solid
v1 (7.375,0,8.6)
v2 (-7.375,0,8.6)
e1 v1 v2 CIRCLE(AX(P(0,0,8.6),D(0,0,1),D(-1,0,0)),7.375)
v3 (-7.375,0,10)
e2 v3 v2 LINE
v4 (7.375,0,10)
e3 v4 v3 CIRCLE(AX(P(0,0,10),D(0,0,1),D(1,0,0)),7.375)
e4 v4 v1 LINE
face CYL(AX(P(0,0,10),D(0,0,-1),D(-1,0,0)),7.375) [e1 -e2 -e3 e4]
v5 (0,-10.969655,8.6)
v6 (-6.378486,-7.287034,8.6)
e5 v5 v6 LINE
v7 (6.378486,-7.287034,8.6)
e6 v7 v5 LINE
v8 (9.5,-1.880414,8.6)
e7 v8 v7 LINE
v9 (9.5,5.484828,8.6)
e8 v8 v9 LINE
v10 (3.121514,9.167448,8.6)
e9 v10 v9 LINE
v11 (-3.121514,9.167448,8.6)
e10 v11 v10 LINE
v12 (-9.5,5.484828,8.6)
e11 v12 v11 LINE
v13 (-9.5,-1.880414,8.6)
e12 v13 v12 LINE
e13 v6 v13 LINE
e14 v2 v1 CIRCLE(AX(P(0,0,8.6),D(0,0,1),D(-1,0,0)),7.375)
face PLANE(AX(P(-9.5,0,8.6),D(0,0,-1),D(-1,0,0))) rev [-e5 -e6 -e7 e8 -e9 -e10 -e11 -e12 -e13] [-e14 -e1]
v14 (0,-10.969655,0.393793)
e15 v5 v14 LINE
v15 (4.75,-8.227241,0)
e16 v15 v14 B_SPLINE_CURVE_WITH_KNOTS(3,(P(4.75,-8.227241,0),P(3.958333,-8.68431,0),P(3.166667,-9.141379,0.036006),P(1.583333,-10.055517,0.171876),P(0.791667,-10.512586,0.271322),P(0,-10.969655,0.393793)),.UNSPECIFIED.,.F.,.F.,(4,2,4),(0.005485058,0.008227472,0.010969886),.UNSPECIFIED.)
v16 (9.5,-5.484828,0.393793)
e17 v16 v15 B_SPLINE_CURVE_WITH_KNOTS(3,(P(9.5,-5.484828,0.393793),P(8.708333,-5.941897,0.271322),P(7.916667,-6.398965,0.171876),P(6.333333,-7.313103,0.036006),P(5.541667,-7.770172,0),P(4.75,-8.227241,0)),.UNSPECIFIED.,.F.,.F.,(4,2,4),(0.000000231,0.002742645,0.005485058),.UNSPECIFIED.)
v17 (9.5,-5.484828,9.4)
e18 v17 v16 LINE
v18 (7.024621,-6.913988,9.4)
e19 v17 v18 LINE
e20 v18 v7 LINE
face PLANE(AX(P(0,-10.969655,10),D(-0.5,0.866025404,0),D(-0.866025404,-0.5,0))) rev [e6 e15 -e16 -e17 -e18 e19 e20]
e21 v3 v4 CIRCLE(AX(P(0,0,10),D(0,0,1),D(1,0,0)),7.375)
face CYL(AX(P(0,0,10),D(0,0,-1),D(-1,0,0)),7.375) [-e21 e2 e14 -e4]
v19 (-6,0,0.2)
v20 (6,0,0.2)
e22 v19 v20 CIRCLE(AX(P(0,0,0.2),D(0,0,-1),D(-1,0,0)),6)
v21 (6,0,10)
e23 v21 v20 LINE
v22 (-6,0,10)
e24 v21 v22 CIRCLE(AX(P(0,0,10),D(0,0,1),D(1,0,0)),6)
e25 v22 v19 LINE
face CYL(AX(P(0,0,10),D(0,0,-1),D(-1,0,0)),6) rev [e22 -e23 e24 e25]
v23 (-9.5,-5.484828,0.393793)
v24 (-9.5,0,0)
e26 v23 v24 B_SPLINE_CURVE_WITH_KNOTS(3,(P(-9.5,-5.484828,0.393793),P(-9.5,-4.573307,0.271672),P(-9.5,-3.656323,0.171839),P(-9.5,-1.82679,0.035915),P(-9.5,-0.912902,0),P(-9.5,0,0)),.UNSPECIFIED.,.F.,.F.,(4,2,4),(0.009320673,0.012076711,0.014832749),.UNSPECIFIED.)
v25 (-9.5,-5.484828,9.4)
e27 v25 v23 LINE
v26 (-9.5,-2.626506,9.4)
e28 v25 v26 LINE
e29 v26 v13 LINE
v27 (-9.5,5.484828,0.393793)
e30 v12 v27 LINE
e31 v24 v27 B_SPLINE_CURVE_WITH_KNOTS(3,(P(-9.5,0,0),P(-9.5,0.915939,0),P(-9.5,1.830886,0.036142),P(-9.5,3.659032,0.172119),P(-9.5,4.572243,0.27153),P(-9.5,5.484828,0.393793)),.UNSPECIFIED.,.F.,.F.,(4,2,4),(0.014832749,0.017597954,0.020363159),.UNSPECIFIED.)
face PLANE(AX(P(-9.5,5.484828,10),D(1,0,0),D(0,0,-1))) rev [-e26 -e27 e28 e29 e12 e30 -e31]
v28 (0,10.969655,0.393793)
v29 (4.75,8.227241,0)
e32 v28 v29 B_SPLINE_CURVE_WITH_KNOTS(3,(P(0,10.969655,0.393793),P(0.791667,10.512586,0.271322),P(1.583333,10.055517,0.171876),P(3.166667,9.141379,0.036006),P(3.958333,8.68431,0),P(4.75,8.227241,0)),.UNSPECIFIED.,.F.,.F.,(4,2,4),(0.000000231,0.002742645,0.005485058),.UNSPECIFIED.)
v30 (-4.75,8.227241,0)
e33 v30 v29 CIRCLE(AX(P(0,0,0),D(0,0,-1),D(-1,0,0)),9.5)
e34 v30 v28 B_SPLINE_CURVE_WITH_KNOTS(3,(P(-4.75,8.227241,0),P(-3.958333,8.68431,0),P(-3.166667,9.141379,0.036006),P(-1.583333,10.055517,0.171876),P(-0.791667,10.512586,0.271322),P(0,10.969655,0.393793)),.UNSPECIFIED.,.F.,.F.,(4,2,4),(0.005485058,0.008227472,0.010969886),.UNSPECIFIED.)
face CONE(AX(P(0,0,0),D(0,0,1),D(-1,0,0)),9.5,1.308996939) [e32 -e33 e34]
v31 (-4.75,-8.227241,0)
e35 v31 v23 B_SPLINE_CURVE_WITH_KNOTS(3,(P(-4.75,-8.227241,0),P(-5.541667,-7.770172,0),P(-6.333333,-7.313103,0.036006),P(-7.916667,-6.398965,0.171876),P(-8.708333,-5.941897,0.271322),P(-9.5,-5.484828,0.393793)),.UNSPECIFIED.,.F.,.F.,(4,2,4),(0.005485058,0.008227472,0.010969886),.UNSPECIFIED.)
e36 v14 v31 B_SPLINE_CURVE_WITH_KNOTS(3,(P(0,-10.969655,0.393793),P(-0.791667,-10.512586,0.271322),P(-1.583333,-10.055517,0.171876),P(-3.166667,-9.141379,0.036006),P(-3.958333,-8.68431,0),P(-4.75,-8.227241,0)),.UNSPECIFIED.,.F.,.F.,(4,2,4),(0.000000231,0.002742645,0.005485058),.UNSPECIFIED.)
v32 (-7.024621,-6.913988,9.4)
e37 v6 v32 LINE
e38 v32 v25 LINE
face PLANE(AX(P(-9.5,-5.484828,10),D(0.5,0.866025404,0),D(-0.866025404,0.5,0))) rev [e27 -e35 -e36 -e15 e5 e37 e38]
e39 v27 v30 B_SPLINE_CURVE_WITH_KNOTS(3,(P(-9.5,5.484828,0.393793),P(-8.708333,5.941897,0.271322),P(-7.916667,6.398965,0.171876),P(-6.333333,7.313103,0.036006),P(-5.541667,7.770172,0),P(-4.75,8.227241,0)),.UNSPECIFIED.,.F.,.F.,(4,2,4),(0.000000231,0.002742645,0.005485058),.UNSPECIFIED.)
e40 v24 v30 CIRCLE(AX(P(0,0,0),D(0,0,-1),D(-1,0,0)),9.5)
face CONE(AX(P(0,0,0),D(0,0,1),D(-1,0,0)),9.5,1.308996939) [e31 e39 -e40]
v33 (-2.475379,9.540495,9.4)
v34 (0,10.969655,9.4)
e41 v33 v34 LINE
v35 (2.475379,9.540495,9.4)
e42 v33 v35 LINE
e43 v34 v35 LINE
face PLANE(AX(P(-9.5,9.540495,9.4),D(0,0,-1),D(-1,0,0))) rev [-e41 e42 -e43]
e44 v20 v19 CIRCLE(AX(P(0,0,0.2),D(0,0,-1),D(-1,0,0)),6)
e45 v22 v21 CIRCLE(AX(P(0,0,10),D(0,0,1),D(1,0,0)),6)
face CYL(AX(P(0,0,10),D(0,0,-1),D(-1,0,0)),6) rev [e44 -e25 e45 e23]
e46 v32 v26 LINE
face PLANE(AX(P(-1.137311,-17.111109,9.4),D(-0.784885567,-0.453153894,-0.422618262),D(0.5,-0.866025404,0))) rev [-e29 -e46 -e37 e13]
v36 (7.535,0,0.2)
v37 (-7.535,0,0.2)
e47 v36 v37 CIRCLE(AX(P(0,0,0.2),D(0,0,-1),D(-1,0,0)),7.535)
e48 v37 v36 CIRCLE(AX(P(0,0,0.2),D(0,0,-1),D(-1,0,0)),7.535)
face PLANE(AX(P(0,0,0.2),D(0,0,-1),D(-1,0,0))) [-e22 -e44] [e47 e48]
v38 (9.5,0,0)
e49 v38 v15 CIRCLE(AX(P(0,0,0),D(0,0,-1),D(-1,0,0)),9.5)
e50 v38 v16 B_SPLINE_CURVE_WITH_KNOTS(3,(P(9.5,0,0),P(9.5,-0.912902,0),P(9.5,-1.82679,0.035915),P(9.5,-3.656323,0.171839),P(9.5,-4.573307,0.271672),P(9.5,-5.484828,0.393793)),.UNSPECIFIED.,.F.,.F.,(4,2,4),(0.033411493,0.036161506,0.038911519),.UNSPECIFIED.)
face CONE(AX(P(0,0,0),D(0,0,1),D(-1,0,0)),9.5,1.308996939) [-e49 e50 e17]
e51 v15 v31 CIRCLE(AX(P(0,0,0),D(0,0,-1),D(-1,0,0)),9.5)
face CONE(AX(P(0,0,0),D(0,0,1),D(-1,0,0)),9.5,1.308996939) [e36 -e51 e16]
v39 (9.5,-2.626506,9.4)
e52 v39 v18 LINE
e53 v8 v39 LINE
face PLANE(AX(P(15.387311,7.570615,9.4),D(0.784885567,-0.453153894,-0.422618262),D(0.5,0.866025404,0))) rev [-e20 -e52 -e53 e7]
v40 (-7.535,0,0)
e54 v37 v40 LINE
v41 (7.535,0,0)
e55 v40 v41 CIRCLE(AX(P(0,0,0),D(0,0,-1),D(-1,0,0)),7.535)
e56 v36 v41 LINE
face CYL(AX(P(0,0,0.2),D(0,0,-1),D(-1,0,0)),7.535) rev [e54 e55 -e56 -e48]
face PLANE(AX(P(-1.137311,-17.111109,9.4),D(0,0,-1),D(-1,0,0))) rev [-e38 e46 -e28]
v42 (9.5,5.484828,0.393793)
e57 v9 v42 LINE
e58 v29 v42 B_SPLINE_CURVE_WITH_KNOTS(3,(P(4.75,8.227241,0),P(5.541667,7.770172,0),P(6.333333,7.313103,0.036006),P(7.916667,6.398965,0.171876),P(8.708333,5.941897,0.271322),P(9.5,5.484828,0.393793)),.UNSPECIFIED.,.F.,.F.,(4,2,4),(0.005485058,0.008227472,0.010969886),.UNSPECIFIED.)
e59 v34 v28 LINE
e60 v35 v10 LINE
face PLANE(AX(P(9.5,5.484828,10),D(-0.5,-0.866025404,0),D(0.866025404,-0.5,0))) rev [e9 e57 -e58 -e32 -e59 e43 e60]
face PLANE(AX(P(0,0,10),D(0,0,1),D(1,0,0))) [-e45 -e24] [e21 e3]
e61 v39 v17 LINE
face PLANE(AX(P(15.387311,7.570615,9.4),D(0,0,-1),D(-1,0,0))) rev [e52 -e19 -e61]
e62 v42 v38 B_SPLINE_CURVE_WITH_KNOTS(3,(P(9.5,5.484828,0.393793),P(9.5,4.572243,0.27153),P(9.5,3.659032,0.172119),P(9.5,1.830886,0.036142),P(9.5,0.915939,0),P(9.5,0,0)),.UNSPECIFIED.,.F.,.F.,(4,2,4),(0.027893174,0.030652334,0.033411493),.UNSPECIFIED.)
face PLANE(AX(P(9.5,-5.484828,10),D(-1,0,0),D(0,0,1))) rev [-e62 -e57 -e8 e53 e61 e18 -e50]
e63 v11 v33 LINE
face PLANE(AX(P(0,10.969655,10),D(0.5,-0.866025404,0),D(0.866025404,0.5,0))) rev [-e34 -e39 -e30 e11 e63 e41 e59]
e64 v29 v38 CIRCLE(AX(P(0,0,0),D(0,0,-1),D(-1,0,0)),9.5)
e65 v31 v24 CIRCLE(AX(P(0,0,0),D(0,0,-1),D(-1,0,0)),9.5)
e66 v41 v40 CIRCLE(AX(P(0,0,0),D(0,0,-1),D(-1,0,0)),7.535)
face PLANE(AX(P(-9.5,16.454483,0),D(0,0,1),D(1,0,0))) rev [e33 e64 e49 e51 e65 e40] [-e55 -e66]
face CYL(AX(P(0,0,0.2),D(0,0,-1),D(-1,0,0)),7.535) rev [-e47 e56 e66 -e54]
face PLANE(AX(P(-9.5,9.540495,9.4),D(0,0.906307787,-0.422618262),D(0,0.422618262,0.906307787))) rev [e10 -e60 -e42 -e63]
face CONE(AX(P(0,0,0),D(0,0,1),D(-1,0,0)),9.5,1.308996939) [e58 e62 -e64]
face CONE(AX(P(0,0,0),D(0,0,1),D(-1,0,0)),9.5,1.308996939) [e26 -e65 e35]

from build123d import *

# Parameters (mm, degrees)
SKETCH_1_R               = 6
EXTRUDE_1_DEPTH          = 10
CUT_EXTRUDE_2_DEPTH      = 18.62337463
PATTERN_CIRCULAR_1_COUNT = 3
SKETCH_2_R               = 7.375
SKETCH_2_R_2             = 6
EXTRUDE_2_DEPTH          = 1.4
SKETCH_4_OUTSIDE_W       = 166.146
SKETCH_4_OUTSIDE_H       = 169.086
SKETCH_4_OUTSIDE_R       = 9.5
CUT_EXTRUDE_3_DEPTH      = 18.62337463
CUT_EXTRUDE_3_DRAFT      = -75
SKETCH_5_R               = 7.535
CUT_EXTRUDE_4_DEPTH      = 0.2


with BuildPart() as part:
    # 草图1 → 拉伸1 (new body)
    with BuildSketch(Plane.XY):
        Polygon((0, 10.969655115), (-9.5, 5.484827557), (-9.5, -5.484827557), (0, -10.969655115), (9.5, -5.484827557), (9.5, 5.484827557), align=None)
        Circle(SKETCH_1_R, mode=Mode.SUBTRACT)
    extrude(amount=EXTRUDE_1_DEPTH)

    # 草图3 → 切除-拉伸2 (cut, symmetric)
    with BuildSketch(Plane(origin=(0, 0, 0), x_dir=(0, 0, -1), z_dir=(1, 0, 0))):
        Polygon((-9.4, 9.540494522), (-8.6, 9.167448395), (-8.6, 0), (-10, 0), (-10, 10.969655115), (-9.4, 10.969655115), align=None)
    cut_extrude_2 = extrude(amount=CUT_EXTRUDE_2_DEPTH, both=True, mode=Mode.SUBTRACT)

    # 阵列(圆周)1: 切除-拉伸2 ×3 about axis
    pattern_circular_1_axis = Axis((0, 0, 0), (0, 0, 1))
    for i in range(1, PATTERN_CIRCULAR_1_COUNT):
        add(cut_extrude_2.rotate(pattern_circular_1_axis, i * 360 / PATTERN_CIRCULAR_1_COUNT), mode=Mode.SUBTRACT)

    # 草图2 → 拉伸2 (add)
    with BuildSketch(Plane.XY.offset(8.6)):
        with Locations(Location((0, 0, 0), (0, 0, 180))):
            Circle(SKETCH_2_R)
        Circle(SKETCH_2_R_2, mode=Mode.SUBTRACT)
    extrude(amount=EXTRUDE_2_DEPTH)


with BuildPart() as cut_extrude_3_tool:
    # 草图4 outside → 切除-拉伸3 (with draft: the straight prism first)
    with BuildSketch(Plane(origin=(0, 0, 0), x_dir=(-1, 0, 0), z_dir=(0, 0, -1))):
        Rectangle(SKETCH_4_OUTSIDE_W, SKETCH_4_OUTSIDE_H)
        Circle(SKETCH_4_OUTSIDE_R, mode=Mode.SUBTRACT)
    extrude(amount=-CUT_EXTRUDE_3_DEPTH)
    # 切除-拉伸3: the draft: its side faces are tilted about the plane it starts from
    cut_extrude_3_sides = [cut_extrude_3_tool.faces().sort_by_distance(p)[0] for p in [
        (0, -84.543, 9.311687315),
        (-83.073, 0, 9.311687315),
        (0, 84.543, 9.311687315),
        (83.073, 0, 9.311687315),
        (9.5, 0, 9.311687315),
    ]]
    draft(cut_extrude_3_sides, Plane(origin=(0, 0, 0), x_dir=(-1, 0, 0), z_dir=(0, 0, -1)), CUT_EXTRUDE_3_DRAFT)


with BuildPart() as part_1:
    add(part.part)

    # 切除-拉伸3: cut by cut_extrude_3_tool
    add(cut_extrude_3_tool.part, mode=Mode.SUBTRACT)

    # 草图5 → 切除-拉伸4 (cut)
    with BuildSketch(Plane(origin=(0, 0, 0), x_dir=(-1, 0, 0), z_dir=(0, 0, -1))):
        Circle(SKETCH_5_R)
    extrude(amount=-CUT_EXTRUDE_4_DEPTH, mode=Mode.SUBTRACT)


solid = part_1.part
